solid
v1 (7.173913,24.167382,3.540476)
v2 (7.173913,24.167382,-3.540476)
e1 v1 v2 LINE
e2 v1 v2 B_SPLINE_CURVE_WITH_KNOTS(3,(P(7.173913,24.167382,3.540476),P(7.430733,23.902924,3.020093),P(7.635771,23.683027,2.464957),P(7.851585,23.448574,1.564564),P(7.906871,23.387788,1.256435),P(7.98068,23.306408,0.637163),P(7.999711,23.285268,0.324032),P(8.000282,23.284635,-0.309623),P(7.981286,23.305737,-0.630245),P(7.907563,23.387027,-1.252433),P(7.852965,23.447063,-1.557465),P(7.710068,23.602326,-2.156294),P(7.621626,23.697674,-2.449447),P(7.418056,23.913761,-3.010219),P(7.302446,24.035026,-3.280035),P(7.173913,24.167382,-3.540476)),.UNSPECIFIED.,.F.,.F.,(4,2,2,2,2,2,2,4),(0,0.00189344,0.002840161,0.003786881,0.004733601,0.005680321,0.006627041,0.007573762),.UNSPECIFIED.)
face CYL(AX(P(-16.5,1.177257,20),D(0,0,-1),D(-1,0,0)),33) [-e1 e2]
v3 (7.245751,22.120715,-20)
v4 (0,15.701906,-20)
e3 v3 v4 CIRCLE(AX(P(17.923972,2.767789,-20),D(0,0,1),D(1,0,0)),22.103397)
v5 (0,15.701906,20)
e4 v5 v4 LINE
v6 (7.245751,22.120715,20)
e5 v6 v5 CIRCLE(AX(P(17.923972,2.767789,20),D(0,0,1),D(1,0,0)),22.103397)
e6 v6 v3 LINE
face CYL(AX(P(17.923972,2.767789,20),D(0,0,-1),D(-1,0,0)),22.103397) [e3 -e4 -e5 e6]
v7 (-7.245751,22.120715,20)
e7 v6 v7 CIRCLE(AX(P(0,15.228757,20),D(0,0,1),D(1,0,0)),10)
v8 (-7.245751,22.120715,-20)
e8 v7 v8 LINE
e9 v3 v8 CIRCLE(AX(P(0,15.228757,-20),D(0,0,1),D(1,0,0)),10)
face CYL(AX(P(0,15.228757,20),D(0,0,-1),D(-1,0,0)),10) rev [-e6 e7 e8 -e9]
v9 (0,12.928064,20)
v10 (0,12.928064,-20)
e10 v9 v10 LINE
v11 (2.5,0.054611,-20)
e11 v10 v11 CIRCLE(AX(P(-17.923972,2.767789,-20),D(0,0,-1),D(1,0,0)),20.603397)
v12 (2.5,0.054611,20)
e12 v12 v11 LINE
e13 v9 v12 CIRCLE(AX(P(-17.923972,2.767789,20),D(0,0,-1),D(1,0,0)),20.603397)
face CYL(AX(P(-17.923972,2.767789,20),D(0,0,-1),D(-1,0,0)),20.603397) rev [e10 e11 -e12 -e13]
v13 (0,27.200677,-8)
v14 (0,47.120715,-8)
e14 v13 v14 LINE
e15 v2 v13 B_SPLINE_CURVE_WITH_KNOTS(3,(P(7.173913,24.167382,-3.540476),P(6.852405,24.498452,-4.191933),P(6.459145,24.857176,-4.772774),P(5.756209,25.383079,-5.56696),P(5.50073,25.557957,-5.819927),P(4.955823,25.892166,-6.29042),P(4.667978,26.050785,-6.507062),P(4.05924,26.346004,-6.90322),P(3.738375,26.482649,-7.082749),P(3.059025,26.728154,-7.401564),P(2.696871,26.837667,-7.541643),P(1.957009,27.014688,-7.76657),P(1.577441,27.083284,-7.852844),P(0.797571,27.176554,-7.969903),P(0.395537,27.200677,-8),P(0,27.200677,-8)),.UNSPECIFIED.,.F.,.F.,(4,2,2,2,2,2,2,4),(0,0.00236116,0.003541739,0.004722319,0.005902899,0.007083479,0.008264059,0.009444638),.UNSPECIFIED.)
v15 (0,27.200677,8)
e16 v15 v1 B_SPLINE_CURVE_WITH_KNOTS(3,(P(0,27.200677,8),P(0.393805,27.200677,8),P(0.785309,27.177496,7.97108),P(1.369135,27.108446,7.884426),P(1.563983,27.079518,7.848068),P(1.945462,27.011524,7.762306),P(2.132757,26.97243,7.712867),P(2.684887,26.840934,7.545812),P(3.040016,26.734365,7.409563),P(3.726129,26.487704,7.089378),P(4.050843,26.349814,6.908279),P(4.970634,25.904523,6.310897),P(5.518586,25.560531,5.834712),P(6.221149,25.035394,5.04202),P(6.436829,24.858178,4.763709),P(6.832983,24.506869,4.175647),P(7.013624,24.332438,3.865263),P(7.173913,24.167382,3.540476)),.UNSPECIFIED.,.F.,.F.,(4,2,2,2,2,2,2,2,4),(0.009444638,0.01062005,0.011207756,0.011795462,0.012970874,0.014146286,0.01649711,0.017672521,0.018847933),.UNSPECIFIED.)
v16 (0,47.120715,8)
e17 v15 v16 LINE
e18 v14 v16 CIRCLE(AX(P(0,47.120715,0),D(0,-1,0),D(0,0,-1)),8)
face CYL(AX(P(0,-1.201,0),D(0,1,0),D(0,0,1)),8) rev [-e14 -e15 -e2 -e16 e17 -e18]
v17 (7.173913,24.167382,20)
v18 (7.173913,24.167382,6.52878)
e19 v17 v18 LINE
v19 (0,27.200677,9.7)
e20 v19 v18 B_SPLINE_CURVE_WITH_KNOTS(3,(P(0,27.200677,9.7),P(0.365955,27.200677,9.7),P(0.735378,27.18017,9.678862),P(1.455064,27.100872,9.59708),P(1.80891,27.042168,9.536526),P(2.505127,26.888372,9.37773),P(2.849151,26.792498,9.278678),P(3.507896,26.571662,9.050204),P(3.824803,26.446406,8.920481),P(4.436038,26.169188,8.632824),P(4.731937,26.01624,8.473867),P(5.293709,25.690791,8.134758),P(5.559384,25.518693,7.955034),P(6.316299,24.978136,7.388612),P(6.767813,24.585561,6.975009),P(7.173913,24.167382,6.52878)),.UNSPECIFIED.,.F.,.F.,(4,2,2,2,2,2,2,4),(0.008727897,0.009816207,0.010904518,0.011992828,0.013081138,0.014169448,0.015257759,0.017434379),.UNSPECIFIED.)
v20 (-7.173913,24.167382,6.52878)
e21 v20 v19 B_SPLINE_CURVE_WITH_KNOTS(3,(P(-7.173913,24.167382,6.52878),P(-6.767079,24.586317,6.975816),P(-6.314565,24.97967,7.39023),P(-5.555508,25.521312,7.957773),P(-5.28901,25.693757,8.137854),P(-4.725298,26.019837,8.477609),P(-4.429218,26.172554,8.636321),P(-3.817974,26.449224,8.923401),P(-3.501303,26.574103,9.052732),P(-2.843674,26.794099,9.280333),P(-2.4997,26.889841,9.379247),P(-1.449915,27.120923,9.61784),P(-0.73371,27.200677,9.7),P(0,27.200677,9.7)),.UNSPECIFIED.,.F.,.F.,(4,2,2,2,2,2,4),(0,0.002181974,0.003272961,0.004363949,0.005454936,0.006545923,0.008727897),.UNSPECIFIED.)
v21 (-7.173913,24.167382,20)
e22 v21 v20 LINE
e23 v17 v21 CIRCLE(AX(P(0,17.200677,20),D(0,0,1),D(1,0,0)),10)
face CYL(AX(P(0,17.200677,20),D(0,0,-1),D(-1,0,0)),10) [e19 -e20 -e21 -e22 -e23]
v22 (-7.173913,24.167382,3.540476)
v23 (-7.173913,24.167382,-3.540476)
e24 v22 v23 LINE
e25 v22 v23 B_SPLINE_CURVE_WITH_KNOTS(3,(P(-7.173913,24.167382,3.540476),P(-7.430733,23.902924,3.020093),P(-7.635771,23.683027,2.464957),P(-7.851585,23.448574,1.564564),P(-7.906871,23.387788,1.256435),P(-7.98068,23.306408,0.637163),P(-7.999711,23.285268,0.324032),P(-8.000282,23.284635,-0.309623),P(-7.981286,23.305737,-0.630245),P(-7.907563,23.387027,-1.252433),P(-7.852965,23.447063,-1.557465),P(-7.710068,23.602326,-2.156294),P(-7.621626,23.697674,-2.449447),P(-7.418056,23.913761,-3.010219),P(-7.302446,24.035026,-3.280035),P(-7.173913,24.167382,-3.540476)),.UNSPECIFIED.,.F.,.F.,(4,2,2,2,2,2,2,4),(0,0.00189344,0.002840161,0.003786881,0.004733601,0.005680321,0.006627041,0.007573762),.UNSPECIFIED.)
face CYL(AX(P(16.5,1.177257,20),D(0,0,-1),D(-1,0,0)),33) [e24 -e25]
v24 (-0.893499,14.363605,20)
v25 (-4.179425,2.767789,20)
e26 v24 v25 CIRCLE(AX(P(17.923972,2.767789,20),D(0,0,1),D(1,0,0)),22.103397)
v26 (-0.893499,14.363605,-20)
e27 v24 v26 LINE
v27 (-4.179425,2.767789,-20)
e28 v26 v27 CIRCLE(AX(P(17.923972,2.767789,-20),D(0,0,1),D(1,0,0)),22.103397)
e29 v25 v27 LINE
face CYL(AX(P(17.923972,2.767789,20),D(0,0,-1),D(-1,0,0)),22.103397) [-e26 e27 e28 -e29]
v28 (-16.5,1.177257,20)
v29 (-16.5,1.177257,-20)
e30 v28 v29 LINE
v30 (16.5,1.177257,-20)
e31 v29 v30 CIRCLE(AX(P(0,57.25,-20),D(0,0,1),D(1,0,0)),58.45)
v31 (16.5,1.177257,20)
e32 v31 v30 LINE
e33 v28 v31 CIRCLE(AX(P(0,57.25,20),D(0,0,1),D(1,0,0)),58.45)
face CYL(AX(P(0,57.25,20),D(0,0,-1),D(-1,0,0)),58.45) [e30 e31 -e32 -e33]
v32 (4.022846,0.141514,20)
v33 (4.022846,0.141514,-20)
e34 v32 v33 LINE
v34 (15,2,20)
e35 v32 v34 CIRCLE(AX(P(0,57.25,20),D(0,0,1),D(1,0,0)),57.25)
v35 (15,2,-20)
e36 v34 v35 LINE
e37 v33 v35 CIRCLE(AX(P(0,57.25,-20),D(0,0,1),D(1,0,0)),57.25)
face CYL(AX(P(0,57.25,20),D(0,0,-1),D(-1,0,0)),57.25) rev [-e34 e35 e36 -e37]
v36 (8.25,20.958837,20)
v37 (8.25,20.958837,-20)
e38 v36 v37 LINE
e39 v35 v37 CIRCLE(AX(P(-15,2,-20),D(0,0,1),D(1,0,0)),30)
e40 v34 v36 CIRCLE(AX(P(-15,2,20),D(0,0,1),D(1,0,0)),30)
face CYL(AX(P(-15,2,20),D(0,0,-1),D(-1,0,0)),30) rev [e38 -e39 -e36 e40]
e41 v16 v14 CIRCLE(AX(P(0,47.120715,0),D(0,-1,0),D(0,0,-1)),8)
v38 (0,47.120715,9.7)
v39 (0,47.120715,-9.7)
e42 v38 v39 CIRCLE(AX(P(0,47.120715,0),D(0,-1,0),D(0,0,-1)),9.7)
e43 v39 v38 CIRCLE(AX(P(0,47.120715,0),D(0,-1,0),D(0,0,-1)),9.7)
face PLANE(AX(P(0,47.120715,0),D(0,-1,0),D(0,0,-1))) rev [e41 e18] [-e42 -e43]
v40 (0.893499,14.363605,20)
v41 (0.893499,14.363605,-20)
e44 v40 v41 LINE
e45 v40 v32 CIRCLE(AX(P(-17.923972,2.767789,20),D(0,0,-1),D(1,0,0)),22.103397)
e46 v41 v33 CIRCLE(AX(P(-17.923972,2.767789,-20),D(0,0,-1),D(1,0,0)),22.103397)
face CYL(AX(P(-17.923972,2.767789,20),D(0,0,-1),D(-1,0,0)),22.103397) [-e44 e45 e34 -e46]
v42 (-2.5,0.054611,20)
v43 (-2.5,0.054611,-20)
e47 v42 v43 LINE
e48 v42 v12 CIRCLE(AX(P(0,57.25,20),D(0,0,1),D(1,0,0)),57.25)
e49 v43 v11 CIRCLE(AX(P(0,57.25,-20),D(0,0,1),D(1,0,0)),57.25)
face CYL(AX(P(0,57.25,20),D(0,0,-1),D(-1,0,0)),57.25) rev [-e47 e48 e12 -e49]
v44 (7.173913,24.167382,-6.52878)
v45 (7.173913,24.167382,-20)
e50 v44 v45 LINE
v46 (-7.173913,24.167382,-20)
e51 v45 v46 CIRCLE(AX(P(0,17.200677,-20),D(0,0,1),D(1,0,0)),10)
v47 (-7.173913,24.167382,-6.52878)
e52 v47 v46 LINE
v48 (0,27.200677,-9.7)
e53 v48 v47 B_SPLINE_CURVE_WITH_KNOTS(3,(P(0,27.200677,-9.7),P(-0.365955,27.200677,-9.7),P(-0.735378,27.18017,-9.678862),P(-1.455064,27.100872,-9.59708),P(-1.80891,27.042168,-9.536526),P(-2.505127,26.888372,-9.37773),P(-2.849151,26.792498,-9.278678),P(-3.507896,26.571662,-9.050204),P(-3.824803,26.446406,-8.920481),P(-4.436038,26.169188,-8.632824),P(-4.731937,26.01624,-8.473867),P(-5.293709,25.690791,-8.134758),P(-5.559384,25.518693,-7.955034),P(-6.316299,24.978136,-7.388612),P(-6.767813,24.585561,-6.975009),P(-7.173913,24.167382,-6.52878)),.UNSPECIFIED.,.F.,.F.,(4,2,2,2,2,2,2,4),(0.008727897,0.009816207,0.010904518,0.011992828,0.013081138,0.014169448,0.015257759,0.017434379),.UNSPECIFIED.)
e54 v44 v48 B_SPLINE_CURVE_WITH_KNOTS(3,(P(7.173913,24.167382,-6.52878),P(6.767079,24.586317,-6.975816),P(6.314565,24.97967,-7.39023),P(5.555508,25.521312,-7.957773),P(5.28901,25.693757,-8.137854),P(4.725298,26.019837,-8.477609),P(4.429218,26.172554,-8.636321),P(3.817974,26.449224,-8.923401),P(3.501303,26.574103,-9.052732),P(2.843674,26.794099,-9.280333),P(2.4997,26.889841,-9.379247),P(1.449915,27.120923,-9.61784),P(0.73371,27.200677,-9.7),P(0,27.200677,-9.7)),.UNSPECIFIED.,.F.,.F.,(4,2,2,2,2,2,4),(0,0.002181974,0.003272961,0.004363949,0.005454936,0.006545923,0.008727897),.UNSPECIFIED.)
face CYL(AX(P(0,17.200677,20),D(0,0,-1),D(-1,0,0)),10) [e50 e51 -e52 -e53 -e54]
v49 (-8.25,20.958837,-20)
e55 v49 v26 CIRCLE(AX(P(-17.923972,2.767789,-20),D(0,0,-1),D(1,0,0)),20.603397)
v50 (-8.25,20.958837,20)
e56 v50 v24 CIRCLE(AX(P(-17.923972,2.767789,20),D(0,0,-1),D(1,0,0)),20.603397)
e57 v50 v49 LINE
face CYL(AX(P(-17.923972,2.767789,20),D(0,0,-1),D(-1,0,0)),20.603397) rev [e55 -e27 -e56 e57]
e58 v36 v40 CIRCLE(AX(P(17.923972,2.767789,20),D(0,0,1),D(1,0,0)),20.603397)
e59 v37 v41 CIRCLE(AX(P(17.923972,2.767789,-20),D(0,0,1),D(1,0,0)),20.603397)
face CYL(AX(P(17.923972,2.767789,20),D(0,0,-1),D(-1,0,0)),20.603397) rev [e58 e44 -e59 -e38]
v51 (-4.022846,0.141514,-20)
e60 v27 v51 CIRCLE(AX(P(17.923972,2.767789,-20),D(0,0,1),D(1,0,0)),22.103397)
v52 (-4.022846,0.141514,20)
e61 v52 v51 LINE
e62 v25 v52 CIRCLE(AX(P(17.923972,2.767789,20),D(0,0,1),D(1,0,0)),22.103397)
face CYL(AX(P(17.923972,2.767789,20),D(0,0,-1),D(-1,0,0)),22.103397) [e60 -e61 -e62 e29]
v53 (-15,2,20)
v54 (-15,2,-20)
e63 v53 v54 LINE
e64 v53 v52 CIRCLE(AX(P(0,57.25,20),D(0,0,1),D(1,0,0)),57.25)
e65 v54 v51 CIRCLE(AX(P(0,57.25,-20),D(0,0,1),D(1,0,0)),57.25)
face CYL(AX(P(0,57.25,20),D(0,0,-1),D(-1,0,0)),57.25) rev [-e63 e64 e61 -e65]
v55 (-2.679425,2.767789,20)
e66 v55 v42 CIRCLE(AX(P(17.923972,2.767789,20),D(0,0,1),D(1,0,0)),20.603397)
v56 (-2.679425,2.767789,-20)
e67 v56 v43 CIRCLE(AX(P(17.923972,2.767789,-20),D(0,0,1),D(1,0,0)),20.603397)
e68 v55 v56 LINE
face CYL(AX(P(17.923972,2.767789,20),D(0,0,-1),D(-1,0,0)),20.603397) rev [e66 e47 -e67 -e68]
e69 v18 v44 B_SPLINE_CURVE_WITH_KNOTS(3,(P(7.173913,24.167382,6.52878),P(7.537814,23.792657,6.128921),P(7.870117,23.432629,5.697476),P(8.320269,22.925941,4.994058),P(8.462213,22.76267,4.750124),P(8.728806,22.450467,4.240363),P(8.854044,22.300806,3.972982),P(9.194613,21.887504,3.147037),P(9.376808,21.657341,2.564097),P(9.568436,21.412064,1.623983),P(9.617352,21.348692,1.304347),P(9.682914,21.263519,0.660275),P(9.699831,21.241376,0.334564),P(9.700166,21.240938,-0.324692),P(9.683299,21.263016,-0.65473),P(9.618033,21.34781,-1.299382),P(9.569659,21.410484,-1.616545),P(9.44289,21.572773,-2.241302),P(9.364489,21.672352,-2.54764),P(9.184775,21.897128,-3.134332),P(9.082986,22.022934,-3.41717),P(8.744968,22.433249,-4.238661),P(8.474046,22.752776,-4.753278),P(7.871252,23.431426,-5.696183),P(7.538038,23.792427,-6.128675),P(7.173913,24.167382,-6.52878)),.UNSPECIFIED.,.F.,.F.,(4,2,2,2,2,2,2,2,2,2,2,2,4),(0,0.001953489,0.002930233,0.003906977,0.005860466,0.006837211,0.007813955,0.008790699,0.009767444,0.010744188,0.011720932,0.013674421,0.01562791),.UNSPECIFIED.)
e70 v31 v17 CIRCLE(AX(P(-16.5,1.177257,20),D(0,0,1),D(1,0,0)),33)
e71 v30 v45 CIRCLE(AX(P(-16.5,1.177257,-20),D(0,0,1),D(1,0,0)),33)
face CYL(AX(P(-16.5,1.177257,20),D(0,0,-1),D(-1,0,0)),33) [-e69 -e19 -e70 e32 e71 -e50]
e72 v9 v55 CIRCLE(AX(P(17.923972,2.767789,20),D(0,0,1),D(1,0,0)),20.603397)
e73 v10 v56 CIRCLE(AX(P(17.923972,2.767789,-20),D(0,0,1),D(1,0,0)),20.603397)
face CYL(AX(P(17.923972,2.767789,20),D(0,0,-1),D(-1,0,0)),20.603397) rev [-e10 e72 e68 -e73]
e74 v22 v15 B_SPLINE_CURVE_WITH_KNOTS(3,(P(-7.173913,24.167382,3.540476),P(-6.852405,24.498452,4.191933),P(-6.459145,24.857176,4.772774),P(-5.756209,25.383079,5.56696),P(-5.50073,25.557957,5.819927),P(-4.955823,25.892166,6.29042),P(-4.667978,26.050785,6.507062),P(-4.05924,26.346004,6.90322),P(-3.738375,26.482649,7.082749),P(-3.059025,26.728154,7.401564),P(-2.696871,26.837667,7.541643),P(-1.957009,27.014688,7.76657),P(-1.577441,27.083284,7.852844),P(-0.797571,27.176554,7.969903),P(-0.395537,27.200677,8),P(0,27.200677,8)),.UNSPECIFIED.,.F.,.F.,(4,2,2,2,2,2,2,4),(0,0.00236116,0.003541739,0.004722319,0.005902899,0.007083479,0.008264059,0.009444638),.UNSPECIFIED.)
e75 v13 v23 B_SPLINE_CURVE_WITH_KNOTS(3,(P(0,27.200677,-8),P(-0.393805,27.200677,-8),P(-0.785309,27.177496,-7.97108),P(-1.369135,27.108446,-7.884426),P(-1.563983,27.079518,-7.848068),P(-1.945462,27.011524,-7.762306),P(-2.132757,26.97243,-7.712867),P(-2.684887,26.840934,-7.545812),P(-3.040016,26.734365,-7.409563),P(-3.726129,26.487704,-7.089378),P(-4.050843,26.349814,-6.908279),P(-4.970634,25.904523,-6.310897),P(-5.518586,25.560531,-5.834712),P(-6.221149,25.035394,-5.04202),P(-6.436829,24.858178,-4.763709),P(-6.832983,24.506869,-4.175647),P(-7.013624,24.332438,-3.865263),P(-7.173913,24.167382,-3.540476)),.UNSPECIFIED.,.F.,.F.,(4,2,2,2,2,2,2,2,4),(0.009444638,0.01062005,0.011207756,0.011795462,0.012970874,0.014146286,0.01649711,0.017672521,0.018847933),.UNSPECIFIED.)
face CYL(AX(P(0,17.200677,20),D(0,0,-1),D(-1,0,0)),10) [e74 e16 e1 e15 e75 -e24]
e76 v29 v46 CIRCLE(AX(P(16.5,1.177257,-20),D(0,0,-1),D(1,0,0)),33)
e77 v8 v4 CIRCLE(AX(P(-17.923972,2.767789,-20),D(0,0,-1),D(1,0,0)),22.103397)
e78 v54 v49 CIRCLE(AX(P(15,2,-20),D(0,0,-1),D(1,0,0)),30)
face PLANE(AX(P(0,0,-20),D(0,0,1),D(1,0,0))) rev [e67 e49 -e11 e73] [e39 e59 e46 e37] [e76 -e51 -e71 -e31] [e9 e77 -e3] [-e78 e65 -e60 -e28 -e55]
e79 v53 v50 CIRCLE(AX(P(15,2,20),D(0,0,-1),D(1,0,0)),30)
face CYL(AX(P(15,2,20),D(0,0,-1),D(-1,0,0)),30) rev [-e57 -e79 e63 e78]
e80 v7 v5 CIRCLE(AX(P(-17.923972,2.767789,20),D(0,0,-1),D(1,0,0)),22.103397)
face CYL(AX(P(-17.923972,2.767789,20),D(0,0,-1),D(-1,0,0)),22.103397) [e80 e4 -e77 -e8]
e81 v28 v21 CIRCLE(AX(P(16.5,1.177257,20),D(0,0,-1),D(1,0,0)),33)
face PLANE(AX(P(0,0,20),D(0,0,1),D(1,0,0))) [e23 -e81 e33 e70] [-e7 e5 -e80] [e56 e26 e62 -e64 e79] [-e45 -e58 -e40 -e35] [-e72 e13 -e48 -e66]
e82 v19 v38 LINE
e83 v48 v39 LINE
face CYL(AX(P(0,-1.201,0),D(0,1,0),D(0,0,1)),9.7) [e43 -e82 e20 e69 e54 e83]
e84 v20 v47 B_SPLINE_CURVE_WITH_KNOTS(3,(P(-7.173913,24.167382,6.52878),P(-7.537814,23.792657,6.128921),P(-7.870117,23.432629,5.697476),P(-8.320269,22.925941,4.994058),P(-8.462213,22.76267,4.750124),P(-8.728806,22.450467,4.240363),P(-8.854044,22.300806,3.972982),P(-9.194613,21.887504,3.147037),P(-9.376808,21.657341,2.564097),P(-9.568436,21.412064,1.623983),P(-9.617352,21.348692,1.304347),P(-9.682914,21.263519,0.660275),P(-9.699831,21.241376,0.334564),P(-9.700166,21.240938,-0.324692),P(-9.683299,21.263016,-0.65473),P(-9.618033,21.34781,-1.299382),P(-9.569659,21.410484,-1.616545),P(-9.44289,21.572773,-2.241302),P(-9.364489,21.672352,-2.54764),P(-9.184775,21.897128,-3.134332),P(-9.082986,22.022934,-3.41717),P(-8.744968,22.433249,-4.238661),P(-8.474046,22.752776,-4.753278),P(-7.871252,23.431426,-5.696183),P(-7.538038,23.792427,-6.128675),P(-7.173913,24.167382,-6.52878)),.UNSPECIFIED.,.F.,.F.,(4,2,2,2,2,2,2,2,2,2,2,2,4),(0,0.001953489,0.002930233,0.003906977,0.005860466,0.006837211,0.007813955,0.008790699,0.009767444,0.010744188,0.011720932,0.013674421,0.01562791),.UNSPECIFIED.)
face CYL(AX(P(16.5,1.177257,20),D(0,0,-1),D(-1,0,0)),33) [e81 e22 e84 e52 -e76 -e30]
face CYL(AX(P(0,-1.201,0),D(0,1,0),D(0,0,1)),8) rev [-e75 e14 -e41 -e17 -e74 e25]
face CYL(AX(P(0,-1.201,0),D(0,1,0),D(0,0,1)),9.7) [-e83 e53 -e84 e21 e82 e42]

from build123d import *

# Parameters (mm, degrees)
EXTRUDE_1182_DEPTH                  = 20
SKETCH_1261_R                       = 9.7
SKETCH_1261_R_2                     = 8
EXTRUDE_1314_DEPTH                  = 25
EXTRUDE_1314_DIRECTION_2_REACH      = 36.873
EXTRUDE_1314_DIRECTION_2_END_RADIUS = 57.25
CUT_EXTRUDE_1_DEPTH                 = 54.783006673
CUT_EXTRUDE_1_DEPTH_BACK            = 54.783006673


with BuildPart() as part:
    # Sketch 176 → Extrude 1182 (new, symmetric)
    with BuildSketch(Plane.XY):
        with BuildLine():
            ThreePointArc((-7.173913043, 24.16738193), (-14.079724741, 13.582112358), (-16.5, 1.177257067))
            ThreePointArc((-16.5, 1.177257067), (0, -1.2), (16.5, 1.177257067))
            ThreePointArc((16.5, 1.177257067), (14.079724741, 13.582112358), (7.173913043, 24.16738193))
            ThreePointArc((7.173913043, 24.16738193), (0, 27.200677426), (-7.173913043, 24.16738193))
        make_face()
        with BuildLine():
            ThreePointArc((-0.89349881, 14.363604773), (-3.663033007, 7.517669831), (-4.022846329, 0.141513701))
            ThreePointArc((-4.022846329, 0.141513701), (-9.556707772, 0.803283208), (-15, 2))
            ThreePointArc((-15, 2), (-13.262165522, 12.062305899), (-8.25, 20.95883699))
            ThreePointArc((-8.25, 20.95883699), (-4.170568058, 18.108709455), (-0.89349881, 14.363604773))
        make_face(mode=Mode.SUBTRACT)
        with BuildLine():
            ThreePointArc((-2.5, 0.0546112), (-2.301572456, 6.695550977), (0, 12.928064021))
            ThreePointArc((0, 12.928064021), (2.301572456, 6.695550977), (2.5, 0.0546112))
            ThreePointArc((2.5, 0.0546112), (0, 0), (-2.5, 0.0546112))
        make_face(mode=Mode.SUBTRACT)
        with BuildLine():
            ThreePointArc((4.022846329, 0.141513701), (3.663033007, 7.517669831), (0.89349881, 14.363604773))
            ThreePointArc((0.89349881, 14.363604773), (4.170568058, 18.108709455), (8.25, 20.95883699))
            ThreePointArc((8.25, 20.95883699), (13.262165522, 12.062305899), (15, 2))
            ThreePointArc((15, 2), (9.556707772, 0.803283208), (4.022846329, 0.141513701))
        make_face(mode=Mode.SUBTRACT)
        with BuildLine():
            ThreePointArc((7.245751005, 22.120715085), (3.267177029, 19.312833939), (0, 15.701905849))
            ThreePointArc((0, 15.701905849), (-3.267177029, 19.312833939), (-7.245751005, 22.120715085))
            ThreePointArc((-7.245751005, 22.120715085), (0, 25.228756555), (7.245751005, 22.120715085))
        make_face(mode=Mode.SUBTRACT)
    extrude(amount=EXTRUDE_1182_DEPTH, both=True)

    # Sketch 1261 → Extrude 1314 (add)
    with BuildSketch(Plane(origin=(0, 22.120715085, 0), x_dir=(-1, 0, 0), z_dir=(0, -1, 0))):
        with Locations(Location((0, 0, 0), (0, 0, 222.304463408))):
            Circle(SKETCH_1261_R)
        with Locations(Location((0, 0, 0), (0, 0, 206.267303198))):
            Circle(SKETCH_1261_R_2, mode=Mode.SUBTRACT)
    extrude(amount=-EXTRUDE_1314_DEPTH)

    # Extrude 1314 direction 2: up to this cylinder (the profile starts inside it)
    extrude_1314_direction_2_end = Plane(origin=(0, 57.25, -6.344118), z_dir=(0, 0, -1)) * Cylinder(EXTRUDE_1314_DIRECTION_2_END_RADIUS, 189.246, mode=Mode.PRIVATE)
    # Sketch 1261 → Extrude 1314 direction 2 (add, up to the surface)
    with BuildSketch(Plane(origin=(0, 22.120715085, 0), x_dir=(-1, 0, 0), z_dir=(0, -1, 0)), mode=Mode.PRIVATE) as extrude_1314_direction_2_sk1:
        with Locations(Location((0, 0, 0), (0, 0, 222.304463408))):
            Circle(SKETCH_1261_R)
        with Locations(Location((0, 0, 0), (0, 0, 206.267303198))):
            Circle(SKETCH_1261_R_2, mode=Mode.SUBTRACT)
    extrude_1314_direction_2_tool1 = extrude(extrude_1314_direction_2_sk1.sketch, amount=EXTRUDE_1314_DIRECTION_2_REACH, mode=Mode.PRIVATE) & extrude_1314_direction_2_end
    add(extrude_1314_direction_2_tool1.solids().sort_by_distance((-6.971004, 22.120715, -6.344118))[0])

    # Sketch 1375 → 切除-拉伸1 (cut, two sides: drawn at the far end of the back side and taken through both)
    with BuildSketch(Plane.XY.offset(-CUT_EXTRUDE_1_DEPTH_BACK)):
        with BuildLine():
            ThreePointArc((4.022846329, 0.141513701), (9.556707772, 0.803283208), (15, 2))
            ThreePointArc((15, 2), (13.262165522, 12.062305899), (8.25, 20.95883699))
            ThreePointArc((8.25, 20.95883699), (4.170568058, 18.108709455), (0.89349881, 14.363604773))
            ThreePointArc((0.89349881, 14.363604773), (3.663033007, 7.517669831), (4.022846329, 0.141513701))
        make_face()
        with BuildLine():
            ThreePointArc((-8.25, 20.95883699), (-13.262165522, 12.062305899), (-15, 2))
            ThreePointArc((-15, 2), (-9.556707772, 0.803283208), (-4.022846329, 0.141513701))
            ThreePointArc((-4.022846329, 0.141513701), (-3.663033007, 7.517669831), (-0.89349881, 14.363604773))
            ThreePointArc((-0.89349881, 14.363604773), (-4.170568058, 18.108709455), (-8.25, 20.95883699))
        make_face()
        with BuildLine():
            ThreePointArc((-2.5, 0.0546112), (0, 0), (2.5, 0.0546112))
            ThreePointArc((2.5, 0.0546112), (2.301572456, 6.695550977), (0, 12.928064021))
            ThreePointArc((0, 12.928064021), (-2.301572456, 6.695550977), (-2.5, 0.0546112))
        make_face()
        with BuildLine():
            ThreePointArc((7.245751005, 22.120715085), (3.267177029, 19.312833939), (0, 15.701905849))
            ThreePointArc((0, 15.701905849), (-3.267177029, 19.312833939), (-7.245751005, 22.120715085))
            ThreePointArc((-7.245751005, 22.120715085), (0, 25.228756555), (7.245751005, 22.120715085))
        make_face()
    extrude(amount=CUT_EXTRUDE_1_DEPTH + CUT_EXTRUDE_1_DEPTH_BACK, mode=Mode.SUBTRACT)


solid = part.part
